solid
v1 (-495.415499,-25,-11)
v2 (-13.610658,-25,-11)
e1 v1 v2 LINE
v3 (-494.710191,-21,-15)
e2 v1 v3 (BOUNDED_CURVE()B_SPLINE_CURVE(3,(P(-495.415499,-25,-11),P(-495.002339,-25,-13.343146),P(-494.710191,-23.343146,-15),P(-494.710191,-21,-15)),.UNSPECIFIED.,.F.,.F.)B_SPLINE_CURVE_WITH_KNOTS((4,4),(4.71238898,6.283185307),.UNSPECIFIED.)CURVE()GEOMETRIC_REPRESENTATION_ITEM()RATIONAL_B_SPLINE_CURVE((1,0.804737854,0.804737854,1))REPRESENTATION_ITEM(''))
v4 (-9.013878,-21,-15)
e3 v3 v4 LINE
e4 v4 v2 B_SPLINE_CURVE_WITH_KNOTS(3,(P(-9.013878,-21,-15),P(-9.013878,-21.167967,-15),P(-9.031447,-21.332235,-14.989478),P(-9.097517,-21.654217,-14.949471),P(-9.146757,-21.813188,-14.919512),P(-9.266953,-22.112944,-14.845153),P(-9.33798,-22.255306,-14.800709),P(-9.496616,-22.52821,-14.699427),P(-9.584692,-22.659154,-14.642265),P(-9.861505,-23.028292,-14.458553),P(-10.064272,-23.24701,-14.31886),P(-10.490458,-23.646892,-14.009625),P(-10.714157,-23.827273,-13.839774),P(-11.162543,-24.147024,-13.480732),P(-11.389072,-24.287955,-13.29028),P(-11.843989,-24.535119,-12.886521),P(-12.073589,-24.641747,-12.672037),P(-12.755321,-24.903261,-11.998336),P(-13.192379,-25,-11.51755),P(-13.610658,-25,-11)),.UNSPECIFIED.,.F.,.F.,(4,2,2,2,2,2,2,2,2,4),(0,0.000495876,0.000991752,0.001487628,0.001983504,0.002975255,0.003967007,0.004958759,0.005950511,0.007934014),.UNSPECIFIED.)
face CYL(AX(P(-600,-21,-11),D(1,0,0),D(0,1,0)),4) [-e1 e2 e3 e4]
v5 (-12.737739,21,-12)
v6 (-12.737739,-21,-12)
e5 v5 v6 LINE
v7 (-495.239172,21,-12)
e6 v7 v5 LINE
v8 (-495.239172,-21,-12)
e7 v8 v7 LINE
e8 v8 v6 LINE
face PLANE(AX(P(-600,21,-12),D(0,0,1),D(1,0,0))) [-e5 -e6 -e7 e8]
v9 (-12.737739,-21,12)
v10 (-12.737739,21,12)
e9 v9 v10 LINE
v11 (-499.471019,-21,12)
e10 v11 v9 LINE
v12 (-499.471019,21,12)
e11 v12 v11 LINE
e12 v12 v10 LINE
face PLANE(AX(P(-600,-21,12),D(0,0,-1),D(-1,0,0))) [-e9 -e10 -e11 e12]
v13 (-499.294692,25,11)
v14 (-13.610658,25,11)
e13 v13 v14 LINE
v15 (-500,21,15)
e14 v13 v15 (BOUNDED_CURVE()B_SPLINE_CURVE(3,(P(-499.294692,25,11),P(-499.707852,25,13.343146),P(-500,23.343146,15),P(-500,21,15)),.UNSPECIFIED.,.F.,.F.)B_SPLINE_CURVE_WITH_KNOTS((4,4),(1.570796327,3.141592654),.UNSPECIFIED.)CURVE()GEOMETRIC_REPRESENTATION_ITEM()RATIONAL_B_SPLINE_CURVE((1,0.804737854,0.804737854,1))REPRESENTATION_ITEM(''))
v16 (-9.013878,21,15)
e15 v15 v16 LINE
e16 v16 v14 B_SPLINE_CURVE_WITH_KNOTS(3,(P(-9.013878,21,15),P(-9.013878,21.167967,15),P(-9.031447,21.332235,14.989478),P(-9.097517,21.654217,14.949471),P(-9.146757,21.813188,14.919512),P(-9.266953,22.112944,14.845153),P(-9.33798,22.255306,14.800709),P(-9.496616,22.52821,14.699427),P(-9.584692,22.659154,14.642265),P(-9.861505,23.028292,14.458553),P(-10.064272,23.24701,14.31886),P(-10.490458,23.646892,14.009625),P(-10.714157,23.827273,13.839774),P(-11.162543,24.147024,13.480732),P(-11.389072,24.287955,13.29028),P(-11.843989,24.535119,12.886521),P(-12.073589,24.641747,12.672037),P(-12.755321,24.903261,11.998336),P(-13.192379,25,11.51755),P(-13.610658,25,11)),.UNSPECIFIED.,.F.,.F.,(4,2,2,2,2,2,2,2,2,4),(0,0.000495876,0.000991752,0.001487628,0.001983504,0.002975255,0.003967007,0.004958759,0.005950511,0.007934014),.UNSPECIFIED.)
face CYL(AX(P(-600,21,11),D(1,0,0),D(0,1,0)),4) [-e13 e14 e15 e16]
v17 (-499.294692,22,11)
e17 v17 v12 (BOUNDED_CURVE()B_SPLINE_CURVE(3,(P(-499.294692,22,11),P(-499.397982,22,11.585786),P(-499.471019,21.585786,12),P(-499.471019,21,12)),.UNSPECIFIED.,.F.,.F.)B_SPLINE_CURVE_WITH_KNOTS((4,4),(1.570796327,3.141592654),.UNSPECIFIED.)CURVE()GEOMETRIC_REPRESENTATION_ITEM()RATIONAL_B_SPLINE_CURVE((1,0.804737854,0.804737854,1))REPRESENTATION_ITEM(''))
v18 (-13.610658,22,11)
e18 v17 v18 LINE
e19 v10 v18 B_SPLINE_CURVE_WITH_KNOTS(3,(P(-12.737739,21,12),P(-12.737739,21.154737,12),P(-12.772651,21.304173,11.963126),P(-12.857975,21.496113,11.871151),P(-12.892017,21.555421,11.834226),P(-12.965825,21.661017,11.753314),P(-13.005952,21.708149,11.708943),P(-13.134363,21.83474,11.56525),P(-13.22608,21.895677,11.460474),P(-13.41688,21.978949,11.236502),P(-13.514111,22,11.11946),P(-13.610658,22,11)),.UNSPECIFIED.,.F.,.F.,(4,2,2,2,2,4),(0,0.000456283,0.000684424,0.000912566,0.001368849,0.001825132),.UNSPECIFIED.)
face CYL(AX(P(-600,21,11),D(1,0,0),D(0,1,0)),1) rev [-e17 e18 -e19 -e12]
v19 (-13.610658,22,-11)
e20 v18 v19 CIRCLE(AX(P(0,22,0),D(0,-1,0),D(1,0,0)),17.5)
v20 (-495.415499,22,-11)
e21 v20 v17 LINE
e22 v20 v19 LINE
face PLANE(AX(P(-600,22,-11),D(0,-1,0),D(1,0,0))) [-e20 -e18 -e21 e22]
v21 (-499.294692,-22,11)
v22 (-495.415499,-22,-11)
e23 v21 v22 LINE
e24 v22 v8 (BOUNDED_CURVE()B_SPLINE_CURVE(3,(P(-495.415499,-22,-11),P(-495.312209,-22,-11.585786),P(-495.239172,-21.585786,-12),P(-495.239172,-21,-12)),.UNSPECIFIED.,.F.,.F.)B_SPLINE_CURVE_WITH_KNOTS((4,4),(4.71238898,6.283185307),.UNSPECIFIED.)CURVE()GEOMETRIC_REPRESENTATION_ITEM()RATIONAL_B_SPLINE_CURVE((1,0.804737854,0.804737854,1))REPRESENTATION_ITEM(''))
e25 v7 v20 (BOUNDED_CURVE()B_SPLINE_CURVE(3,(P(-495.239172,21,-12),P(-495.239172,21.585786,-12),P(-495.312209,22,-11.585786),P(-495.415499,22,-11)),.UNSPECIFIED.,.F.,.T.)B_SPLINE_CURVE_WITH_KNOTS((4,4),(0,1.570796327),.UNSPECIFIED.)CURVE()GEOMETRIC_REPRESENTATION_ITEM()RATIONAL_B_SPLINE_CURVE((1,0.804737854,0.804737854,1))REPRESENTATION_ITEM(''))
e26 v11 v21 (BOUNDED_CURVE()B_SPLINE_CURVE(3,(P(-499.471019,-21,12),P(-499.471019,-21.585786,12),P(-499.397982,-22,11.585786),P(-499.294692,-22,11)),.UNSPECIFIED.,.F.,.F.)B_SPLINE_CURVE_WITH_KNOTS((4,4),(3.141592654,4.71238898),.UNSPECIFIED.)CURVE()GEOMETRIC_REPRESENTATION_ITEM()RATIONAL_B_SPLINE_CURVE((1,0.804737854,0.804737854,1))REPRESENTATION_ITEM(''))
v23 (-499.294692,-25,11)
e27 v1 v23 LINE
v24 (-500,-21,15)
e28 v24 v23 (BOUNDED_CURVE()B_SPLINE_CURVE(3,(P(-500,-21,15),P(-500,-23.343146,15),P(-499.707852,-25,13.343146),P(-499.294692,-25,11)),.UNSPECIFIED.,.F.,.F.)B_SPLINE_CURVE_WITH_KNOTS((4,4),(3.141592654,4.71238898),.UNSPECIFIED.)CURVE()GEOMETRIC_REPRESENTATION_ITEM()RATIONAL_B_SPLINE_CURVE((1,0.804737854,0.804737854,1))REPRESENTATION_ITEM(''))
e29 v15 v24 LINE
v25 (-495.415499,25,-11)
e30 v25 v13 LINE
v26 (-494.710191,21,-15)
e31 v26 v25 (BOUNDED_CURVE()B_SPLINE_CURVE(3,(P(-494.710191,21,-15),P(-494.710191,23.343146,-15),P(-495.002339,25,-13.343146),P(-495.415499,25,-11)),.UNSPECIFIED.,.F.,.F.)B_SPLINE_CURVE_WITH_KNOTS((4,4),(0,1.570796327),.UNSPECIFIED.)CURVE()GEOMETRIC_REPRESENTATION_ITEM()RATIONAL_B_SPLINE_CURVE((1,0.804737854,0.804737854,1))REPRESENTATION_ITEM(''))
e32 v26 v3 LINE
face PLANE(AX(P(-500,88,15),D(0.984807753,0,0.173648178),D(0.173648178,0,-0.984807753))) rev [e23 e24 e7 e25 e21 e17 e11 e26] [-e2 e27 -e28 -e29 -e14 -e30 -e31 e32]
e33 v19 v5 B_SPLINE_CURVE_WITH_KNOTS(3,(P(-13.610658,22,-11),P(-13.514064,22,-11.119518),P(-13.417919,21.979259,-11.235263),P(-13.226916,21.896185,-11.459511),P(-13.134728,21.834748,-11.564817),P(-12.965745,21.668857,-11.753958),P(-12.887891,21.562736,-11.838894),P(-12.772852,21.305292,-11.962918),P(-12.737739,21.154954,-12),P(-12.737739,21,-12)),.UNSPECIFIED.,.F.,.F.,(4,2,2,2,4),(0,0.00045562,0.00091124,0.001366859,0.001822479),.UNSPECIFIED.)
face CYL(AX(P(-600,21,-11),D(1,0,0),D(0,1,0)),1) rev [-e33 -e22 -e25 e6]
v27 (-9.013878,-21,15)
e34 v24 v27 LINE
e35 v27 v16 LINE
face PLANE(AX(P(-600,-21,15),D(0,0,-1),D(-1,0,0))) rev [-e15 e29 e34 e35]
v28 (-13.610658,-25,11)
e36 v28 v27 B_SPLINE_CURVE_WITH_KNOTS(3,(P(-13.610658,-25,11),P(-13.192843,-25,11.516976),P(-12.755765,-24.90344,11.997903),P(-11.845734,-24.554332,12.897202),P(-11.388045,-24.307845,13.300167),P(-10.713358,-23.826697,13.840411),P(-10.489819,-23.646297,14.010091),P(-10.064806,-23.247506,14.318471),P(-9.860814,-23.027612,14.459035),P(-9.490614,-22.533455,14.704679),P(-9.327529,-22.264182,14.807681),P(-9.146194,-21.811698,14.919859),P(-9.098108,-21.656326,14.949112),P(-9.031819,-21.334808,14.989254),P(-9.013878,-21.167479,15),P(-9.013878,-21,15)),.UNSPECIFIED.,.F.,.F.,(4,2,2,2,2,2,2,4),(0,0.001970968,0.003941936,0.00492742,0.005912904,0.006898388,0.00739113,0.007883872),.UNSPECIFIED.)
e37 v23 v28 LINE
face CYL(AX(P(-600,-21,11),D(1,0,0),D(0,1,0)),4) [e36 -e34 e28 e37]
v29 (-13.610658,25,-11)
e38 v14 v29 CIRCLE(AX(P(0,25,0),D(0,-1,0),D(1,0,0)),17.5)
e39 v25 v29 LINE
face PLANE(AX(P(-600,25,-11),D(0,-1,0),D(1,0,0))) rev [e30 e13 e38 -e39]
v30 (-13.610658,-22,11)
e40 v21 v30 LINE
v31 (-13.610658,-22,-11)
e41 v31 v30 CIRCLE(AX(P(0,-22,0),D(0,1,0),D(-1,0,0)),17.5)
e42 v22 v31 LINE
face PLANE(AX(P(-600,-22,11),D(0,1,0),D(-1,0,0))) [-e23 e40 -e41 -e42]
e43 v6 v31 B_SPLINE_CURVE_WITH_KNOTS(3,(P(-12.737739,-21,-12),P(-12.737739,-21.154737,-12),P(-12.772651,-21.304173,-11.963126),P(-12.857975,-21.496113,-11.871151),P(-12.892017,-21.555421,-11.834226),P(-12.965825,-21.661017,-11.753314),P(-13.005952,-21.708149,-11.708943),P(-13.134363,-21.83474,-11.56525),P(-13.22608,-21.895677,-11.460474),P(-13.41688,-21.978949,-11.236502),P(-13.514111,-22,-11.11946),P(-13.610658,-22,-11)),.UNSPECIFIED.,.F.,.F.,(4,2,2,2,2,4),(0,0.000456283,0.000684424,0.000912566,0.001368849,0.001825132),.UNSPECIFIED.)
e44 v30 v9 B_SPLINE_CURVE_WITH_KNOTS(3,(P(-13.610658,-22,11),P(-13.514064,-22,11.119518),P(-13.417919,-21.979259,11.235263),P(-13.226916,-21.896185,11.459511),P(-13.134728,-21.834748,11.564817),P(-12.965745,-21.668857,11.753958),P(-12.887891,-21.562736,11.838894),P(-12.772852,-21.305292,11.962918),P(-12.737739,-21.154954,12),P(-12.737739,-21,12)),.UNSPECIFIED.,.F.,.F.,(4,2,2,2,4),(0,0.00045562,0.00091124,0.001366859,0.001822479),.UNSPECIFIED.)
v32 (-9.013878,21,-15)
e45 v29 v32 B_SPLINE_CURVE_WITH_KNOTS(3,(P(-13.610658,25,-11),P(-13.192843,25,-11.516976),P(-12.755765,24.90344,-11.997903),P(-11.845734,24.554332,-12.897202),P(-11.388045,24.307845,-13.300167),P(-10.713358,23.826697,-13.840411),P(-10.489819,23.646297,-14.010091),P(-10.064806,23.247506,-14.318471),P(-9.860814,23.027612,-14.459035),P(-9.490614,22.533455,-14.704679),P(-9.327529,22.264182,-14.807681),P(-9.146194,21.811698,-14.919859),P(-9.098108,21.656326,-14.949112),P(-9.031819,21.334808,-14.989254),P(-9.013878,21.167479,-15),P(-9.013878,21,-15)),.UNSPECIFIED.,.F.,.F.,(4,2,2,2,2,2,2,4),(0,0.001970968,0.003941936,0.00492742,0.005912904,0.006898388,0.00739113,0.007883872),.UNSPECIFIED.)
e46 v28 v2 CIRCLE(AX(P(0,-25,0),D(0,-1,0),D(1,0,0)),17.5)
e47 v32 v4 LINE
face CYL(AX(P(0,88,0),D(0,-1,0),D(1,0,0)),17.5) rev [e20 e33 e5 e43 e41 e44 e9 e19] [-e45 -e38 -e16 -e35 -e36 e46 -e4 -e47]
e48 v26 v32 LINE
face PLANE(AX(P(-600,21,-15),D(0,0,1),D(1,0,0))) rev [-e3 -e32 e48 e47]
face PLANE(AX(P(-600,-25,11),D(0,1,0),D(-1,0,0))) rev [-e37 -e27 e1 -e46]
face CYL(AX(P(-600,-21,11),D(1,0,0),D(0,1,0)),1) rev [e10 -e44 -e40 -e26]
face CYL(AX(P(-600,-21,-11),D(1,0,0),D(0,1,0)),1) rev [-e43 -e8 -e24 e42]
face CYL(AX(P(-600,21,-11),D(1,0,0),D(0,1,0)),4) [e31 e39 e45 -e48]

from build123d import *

# Parameters (mm, degrees)
SQUARE_TUBE_30_X_30_X_2_6_15_DEPTH = 600
CUT_EXTRUDE3_DEPTH                 = 113
SKETCH13_R                         = 17.5
CUT_EXTRUDE4_DEPTH                 = 113


with BuildPart() as part:
    # Sketch1 → Square tube 30 X 30 X 2.6(15) (new body)
    with BuildSketch(Plane(origin=(0, 0, 0), x_dir=(0, -1, 0), z_dir=(-1, 0, 0))):
        with BuildLine():
            Line((-21, -15), (21, -15))
            ThreePointArc((21, -15), (23.828427125, -13.828427125), (25, -11))
            Line((25, -11), (25, 11))
            ThreePointArc((25, 11), (23.828427125, 13.828427125), (21, 15))
            Line((21, 15), (-21, 15))
            ThreePointArc((-21, 15), (-23.828427125, 13.828427125), (-25, 11))
            Line((-25, 11), (-25, -11))
            ThreePointArc((-25, -11), (-23.828427125, -13.828427125), (-21, -15))
        make_face()
        with BuildLine():
            Line((-21, -12), (21, -12))
            ThreePointArc((21, -12), (21.707106781, -11.707106781), (22, -11))
            Line((22, -11), (22, 11))
            ThreePointArc((22, 11), (21.707106781, 11.707106781), (21, 12))
            Line((21, 12), (-21, 12))
            ThreePointArc((-21, 12), (-21.707106781, 11.707106781), (-22, 11))
            Line((-22, 11), (-22, -11))
            ThreePointArc((-22, -11), (-21.707106781, -11.707106781), (-21, -12))
        make_face(mode=Mode.SUBTRACT)
    extrude(amount=SQUARE_TUBE_30_X_30_X_2_6_15_DEPTH)

    # Sketch12 → Cut-Extrude3 (cut)
    with BuildSketch(Plane.XZ.offset(25)):
        Polygon((-500, 15), (-494.710190579, -15), (-600, -15), (-600, 15), align=None)
    extrude(amount=-CUT_EXTRUDE3_DEPTH, mode=Mode.SUBTRACT)

    # Sketch13 → Cut-Extrude4 (cut)
    with BuildSketch(Plane.XZ.offset(25)):
        Circle(SKETCH13_R)
    extrude(amount=-CUT_EXTRUDE4_DEPTH, mode=Mode.SUBTRACT)


solid = part.part
